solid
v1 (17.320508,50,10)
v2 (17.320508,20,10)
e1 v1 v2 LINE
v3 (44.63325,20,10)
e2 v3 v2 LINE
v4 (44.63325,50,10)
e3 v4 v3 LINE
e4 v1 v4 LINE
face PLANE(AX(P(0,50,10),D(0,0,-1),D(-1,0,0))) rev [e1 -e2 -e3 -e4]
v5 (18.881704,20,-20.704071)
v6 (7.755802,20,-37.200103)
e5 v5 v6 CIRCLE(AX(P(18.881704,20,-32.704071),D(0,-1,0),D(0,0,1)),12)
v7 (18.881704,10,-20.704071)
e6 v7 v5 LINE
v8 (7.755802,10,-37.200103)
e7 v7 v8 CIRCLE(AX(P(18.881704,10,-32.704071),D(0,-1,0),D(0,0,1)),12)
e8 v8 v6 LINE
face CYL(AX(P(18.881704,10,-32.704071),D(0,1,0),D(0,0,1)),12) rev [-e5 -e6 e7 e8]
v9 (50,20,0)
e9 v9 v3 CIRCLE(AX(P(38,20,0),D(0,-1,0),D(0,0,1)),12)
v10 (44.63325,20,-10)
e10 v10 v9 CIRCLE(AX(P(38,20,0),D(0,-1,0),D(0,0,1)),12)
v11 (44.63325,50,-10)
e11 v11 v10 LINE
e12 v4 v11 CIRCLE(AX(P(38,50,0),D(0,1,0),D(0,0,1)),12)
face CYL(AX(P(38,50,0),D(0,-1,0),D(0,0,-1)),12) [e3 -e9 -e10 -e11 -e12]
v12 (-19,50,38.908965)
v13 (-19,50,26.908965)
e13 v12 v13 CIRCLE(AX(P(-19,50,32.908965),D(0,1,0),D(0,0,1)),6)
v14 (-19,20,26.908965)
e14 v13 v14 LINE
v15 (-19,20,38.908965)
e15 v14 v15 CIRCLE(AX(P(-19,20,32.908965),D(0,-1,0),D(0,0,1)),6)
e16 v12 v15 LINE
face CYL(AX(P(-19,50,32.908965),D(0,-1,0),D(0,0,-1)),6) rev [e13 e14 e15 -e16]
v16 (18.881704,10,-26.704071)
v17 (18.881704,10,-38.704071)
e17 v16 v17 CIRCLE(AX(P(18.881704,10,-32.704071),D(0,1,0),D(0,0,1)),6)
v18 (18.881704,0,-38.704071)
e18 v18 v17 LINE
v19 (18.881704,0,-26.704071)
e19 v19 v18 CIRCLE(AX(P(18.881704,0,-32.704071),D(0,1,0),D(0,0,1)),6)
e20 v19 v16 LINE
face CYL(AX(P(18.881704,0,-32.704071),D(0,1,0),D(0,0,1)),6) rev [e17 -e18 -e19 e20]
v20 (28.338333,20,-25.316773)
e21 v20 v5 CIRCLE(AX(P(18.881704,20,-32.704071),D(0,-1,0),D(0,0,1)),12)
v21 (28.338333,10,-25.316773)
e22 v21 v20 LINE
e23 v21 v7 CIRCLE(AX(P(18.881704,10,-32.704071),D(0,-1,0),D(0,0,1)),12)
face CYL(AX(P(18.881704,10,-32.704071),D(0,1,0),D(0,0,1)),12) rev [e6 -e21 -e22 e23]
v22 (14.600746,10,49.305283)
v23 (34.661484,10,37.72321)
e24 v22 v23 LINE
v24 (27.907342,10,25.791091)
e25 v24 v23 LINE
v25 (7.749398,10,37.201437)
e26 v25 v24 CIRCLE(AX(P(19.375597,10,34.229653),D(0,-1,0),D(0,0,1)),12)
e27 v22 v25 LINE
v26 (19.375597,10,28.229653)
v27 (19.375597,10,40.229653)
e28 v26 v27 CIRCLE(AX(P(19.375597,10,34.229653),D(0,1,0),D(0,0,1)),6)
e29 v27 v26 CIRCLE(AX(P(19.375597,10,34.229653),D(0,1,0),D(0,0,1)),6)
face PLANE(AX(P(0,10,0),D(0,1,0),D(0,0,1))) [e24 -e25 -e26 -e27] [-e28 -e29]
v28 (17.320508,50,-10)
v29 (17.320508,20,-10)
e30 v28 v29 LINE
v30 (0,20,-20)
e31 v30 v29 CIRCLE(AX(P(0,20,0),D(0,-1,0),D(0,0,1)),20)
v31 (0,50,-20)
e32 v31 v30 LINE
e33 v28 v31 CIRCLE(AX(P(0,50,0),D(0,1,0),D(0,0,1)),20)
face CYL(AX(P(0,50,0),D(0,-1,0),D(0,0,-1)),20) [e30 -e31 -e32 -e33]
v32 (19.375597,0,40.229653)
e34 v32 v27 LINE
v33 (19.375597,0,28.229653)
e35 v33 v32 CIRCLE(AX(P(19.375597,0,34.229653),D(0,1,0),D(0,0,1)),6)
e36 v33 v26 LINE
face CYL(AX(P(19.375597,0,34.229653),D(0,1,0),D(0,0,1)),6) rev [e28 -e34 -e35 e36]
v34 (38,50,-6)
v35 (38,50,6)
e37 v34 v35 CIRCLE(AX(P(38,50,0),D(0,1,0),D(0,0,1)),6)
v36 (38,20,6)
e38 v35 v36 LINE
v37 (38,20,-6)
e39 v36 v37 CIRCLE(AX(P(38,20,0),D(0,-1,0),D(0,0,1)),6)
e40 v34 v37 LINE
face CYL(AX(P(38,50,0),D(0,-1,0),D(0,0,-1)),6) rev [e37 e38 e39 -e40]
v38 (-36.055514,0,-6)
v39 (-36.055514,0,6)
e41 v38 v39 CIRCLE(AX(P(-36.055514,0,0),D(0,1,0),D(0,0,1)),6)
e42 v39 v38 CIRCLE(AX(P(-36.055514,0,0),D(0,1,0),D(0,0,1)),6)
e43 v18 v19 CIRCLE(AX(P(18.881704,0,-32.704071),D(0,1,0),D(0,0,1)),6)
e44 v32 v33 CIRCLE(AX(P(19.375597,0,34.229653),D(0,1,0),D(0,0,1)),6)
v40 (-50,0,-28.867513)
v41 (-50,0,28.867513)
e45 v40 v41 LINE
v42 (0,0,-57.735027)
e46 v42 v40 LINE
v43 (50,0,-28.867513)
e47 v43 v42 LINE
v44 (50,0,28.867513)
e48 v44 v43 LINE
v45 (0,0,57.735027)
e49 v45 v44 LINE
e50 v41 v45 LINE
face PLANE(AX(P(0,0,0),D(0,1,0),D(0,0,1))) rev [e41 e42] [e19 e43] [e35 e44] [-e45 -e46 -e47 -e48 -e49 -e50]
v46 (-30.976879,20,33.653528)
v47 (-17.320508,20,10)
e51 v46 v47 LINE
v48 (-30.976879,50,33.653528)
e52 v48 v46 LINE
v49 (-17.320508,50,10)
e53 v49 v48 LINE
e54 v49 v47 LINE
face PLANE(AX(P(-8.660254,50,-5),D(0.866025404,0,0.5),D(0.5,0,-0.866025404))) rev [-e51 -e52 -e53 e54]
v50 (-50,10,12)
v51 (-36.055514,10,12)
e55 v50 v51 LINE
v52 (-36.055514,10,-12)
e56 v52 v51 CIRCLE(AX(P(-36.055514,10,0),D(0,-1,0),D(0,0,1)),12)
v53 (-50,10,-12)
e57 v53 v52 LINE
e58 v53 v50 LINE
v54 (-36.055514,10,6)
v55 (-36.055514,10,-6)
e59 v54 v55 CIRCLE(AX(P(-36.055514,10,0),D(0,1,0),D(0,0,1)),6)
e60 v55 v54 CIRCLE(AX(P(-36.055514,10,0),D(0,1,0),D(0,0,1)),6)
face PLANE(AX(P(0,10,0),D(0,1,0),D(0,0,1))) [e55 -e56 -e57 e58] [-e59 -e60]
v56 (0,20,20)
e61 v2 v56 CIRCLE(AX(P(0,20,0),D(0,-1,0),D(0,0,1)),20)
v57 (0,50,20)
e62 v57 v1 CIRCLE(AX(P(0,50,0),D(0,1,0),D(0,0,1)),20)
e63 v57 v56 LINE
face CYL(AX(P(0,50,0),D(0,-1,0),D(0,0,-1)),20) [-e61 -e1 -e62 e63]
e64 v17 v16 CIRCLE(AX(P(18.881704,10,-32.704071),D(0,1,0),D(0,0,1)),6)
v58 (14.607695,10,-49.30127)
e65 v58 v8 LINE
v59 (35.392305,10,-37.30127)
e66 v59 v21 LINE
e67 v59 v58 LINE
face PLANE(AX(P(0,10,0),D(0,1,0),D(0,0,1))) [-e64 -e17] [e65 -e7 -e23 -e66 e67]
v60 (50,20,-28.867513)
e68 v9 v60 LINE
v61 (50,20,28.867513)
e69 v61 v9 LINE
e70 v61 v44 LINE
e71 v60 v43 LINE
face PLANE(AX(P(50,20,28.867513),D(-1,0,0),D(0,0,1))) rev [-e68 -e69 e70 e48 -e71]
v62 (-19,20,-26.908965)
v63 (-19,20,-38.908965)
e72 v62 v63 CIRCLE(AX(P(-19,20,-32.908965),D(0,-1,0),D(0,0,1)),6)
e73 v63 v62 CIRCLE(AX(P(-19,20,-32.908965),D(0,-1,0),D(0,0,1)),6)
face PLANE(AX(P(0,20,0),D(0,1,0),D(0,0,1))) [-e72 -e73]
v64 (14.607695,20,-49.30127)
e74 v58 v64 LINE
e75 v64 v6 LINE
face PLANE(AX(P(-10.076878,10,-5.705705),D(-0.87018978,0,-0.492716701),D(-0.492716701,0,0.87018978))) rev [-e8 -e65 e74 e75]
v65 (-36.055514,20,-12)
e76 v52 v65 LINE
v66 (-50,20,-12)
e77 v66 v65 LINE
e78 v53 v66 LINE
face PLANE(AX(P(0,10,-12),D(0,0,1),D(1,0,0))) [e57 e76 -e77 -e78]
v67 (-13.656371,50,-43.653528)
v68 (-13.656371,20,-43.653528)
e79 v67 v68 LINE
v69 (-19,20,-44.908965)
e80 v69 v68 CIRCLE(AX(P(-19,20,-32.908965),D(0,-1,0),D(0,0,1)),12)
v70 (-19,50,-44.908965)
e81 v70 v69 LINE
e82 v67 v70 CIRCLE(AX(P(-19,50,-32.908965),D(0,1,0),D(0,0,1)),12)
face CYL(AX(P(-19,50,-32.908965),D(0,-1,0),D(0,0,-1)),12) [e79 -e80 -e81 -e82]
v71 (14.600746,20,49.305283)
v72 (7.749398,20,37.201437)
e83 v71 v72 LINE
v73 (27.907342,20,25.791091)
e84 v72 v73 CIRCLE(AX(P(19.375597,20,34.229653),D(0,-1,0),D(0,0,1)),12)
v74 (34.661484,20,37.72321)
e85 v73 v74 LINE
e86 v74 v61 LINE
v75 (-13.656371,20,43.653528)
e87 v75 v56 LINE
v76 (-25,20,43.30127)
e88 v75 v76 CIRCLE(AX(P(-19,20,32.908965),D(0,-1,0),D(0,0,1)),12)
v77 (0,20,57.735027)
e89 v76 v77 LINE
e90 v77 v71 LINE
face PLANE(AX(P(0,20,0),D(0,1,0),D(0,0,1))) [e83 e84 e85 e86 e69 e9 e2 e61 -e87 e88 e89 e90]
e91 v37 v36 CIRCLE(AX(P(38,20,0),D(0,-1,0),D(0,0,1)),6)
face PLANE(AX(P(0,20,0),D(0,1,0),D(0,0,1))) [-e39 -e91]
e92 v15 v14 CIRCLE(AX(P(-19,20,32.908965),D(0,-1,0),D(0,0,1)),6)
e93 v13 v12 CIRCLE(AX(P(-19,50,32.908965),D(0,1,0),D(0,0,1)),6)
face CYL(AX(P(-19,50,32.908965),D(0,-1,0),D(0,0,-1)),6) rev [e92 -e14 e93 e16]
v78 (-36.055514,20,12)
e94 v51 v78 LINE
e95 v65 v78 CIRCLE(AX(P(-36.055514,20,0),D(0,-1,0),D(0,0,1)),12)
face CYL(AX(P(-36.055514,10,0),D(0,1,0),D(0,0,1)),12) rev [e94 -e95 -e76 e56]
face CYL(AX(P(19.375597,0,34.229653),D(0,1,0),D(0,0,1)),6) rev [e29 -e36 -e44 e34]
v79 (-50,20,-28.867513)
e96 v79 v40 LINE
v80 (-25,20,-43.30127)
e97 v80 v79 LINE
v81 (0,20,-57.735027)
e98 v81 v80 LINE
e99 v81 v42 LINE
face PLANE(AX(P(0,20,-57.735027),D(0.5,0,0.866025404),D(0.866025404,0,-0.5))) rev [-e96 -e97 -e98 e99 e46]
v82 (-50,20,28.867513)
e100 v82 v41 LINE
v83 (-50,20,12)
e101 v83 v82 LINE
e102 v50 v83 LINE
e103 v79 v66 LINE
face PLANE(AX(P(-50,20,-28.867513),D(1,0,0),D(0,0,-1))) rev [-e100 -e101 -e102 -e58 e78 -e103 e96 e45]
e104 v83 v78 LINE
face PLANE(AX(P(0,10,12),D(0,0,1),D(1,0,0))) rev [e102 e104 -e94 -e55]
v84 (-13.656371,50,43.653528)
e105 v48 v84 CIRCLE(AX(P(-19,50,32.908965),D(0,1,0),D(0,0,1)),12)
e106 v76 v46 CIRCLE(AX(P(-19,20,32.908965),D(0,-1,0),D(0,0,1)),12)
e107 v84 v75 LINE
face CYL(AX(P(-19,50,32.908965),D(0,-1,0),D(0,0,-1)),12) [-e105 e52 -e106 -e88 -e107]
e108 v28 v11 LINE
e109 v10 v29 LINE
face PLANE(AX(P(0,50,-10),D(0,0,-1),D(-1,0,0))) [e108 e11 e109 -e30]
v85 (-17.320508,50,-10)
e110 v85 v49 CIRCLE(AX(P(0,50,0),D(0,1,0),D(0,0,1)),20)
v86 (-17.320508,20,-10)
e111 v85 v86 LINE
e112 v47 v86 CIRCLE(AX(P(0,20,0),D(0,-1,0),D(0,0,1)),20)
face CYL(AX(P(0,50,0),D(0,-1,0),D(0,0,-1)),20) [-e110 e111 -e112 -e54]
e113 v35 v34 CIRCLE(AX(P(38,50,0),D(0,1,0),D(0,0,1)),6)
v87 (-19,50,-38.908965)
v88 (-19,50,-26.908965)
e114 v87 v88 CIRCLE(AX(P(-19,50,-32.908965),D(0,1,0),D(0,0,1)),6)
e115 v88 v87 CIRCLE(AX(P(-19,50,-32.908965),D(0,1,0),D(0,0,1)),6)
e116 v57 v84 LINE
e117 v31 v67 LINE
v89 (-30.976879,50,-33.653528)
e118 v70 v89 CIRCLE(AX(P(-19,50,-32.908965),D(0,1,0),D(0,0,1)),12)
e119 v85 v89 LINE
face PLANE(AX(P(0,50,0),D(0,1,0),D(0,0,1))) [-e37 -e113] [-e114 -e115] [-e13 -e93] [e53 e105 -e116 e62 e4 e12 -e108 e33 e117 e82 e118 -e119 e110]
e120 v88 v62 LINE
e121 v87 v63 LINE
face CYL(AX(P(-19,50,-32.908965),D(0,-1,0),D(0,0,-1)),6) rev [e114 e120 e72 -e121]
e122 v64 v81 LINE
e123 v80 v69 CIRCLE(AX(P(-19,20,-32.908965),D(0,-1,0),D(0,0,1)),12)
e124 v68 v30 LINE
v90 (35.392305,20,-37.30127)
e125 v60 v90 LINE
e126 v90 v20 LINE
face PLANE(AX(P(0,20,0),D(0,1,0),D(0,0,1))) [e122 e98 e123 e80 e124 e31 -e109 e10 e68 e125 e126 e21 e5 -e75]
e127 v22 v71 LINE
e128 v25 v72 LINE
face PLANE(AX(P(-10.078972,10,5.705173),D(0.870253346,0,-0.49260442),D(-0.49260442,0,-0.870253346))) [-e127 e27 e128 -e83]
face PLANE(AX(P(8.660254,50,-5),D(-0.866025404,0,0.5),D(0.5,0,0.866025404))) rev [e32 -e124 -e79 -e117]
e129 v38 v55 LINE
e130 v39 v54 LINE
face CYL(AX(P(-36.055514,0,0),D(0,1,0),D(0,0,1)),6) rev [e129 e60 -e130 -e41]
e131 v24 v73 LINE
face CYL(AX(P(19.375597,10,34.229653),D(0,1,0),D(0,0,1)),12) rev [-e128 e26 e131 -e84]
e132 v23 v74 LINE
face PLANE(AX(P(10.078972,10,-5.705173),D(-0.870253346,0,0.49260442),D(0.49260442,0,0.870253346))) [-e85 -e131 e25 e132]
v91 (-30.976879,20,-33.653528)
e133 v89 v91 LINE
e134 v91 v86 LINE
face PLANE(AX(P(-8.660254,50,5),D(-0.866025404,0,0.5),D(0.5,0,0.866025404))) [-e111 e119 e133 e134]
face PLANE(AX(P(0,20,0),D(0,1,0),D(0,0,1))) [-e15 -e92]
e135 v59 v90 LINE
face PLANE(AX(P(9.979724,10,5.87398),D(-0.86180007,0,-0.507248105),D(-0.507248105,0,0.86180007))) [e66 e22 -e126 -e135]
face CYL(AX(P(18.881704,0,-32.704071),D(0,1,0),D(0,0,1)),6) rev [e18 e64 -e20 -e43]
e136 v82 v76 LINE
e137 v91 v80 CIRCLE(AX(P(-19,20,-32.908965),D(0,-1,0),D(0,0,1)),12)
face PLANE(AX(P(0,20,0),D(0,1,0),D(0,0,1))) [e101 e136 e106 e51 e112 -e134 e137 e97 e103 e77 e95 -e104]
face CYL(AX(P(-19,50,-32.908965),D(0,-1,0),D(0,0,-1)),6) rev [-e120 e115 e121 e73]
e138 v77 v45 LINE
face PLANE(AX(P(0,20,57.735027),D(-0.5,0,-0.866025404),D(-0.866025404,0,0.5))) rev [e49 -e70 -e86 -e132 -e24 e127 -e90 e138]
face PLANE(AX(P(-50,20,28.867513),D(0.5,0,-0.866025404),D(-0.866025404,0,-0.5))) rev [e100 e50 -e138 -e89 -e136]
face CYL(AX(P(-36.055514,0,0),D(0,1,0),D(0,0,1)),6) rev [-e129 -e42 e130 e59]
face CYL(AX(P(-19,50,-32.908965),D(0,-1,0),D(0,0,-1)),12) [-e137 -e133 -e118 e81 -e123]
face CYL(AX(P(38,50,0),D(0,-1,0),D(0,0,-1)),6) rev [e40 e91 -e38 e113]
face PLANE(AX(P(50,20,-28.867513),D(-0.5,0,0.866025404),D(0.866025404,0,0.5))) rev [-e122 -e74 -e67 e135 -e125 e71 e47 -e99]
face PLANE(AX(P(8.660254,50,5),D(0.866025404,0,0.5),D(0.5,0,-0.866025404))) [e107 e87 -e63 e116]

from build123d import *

# Parameters (mm, degrees)
HEX_BASE_100AF_X20_DEPTH    = 20
EDGE_POCKET_SKETCH_R        = 6
EDGE_POCKETS_DEPTH_10_DEPTH = 10
THREE_ARM_BOSS_SKETCH_R     = 6
THREE_ARM_BOSS_H50_DEPTH    = 50
POCKET_HOLE_SKETCH_R        = 6
POCKET_THROUGH_HOLES_DEPTH  = 10


with BuildPart() as part:
    # Hex Base Sketch → Hex Base 100AF x20 (new body)
    with BuildSketch(Plane(origin=(0, 0, 0), x_dir=(1, 0, 0), z_dir=(0, 1, 0))):
        Polygon((0, 57.735026919), (-50, 28.867513459), (-50, -28.867513459), (0, -57.735026919), (50, -28.867513459), (50, 28.867513459), align=None)
    extrude(amount=HEX_BASE_100AF_X20_DEPTH)

    # Edge Pocket Sketch → Edge Pockets Depth 10 (cut)
    # profile 1 of 6: a face of its own
    with BuildSketch(Plane(origin=(0, 20, 0), x_dir=(1, 0, 0), z_dir=(0, 1, 0))):
        with BuildLine():
            Line((-50, 12), (-50, -12))
            Line((-50, -12), (-36.055514092, -12))
            ThreePointArc((-36.055514092, -12), (-24.055514092, 0), (-36.055514092, 12))
            Line((-36.055514092, 12), (-50, 12))
        make_face()
        with Locations((-38.000001269, 0)):
            Circle(EDGE_POCKET_SKETCH_R, mode=Mode.SUBTRACT)
    # profile 2 of 6: a face of its own
    with BuildSketch(Plane(origin=(0, 20, 0), x_dir=(1, 0, 0), z_dir=(0, 1, 0))):
        with BuildLine():
            Line((35.392304845, 37.301270189), (14.607695155, 49.301270189))
            Line((14.607695155, 49.301270189), (7.755802012, 37.200102575))
            ThreePointArc((7.755802012, 37.200102575), (12.881704296, 22.311766329), (28.338332848, 25.316772856))
            Line((28.338332848, 25.316772856), (35.392304845, 37.301270189))
        make_face()
        with Locations((19.000000635, 32.908966443)):
            Circle(EDGE_POCKET_SKETCH_R, mode=Mode.SUBTRACT)
    # profile 3 of 6: a face of its own
    with BuildSketch(Plane(origin=(0, 20, 0), x_dir=(1, 0, 0), z_dir=(0, 1, 0))):
        with BuildLine():
            ThreePointArc((27.907341935, -25.791090759), (21.025211471, -22.343578273), (13.464344244, -23.786612875))
            ThreePointArc((13.464344244, -23.786612875), (8.335672837, -29.526455354), (7.749398434, -37.201437074))
            Line((7.749398434, -37.201437074), (8.639996816, -38.774801402))
            Line((8.639996816, -38.774801402), (14.600745568, -49.305282535))
            Line((14.600745568, -49.305282535), (34.661483865, -37.723209879))
            Line((34.661483865, -37.723209879), (28.797940317, -27.364455088))
            Line((28.797940317, -27.364455088), (27.907341935, -25.791090759))
        make_face()
        with BuildLine():
            ThreePointArc((24.718968567, -33.069628245), (15.696863266, -38.252955318), (15.763342049, -27.84810817))
            ThreePointArc((15.763342049, -27.84810817), (21.741073867, -27.886301171), (24.718968567, -33.069628245))
        make_face(mode=Mode.SUBTRACT)
    # profile 4 of 6: a face of its own
    with BuildSketch(Plane(origin=(0, 20, 0), x_dir=(1, 0, 0), z_dir=(0, 1, 0))):
        with Locations((18.718968567, -33.069628245)):
            Circle(EDGE_POCKET_SKETCH_R)
    # profile 5 of 6: a face of its own
    with BuildSketch(Plane(origin=(0, 20, 0), x_dir=(1, 0, 0), z_dir=(0, 1, 0))):
        with Locations((-38.000001269, 0)):
            Circle(EDGE_POCKET_SKETCH_R)
    # profile 6 of 6: a face of its own
    with BuildSketch(Plane(origin=(0, 20, 0), x_dir=(1, 0, 0), z_dir=(0, 1, 0))):
        with Locations((19.000000635, 32.908966443)):
            Circle(EDGE_POCKET_SKETCH_R)
    extrude(amount=-EDGE_POCKETS_DEPTH_10_DEPTH, mode=Mode.SUBTRACT)

    # Three-Arm Boss Sketch → Three-Arm Boss H50 (add)
    # profile 1 of 2: a face of its own
    with BuildSketch(Plane(origin=(0, 0, 0), x_dir=(1, 0, 0), z_dir=(0, 1, 0))):
        with BuildLine():
            ThreePointArc((0, -20), (10, -17.320508076), (17.320508076, -10))
            Line((17.320508076, -10), (25, -10))
            Line((25, -10), (25, 10))
            Line((25, 10), (17.320508076, 10))
            ThreePointArc((17.320508076, 10), (10, 17.320508076), (0, 20))
            Line((0, 20), (-13.656370753, 43.65352799))
            ThreePointArc((-13.656370753, 43.65352799), (-25, 43.301270189), (-30.976878828, 33.65352799))
            Line((-30.976878828, 33.65352799), (-17.320508076, 10))
            ThreePointArc((-17.320508076, 10), (-20, 0), (-17.320508076, -10))
            Line((-17.320508076, -10), (-30.976878828, -33.65352799))
            ThreePointArc((-30.976878828, -33.65352799), (-25, -43.301270189), (-13.656370753, -43.65352799))
            Line((-13.656370753, -43.65352799), (0, -20))
        make_face()
        with Locations(Location((-19, -32.908965344, 0), (0, 0, 270))):
            Circle(THREE_ARM_BOSS_SKETCH_R, mode=Mode.SUBTRACT)
        with Locations(Location((-19, 32.908965344, 0), (0, 0, 270))):
            Circle(THREE_ARM_BOSS_SKETCH_R, mode=Mode.SUBTRACT)
    # profile 2 of 2: a face of its own
    with BuildSketch(Plane(origin=(0, 0, 0), x_dir=(1, 0, 0), z_dir=(0, 1, 0))):
        with BuildLine():
            Line((25, 10), (25, -10))
            Line((25, -10), (44.633249581, -10))
            ThreePointArc((44.633249581, -10), (50, 0), (44.633249581, 10))
            Line((44.633249581, 10), (25, 10))
        make_face()
        with Locations(Location((38, 0, 0), (0, 0, 270))):
            Circle(THREE_ARM_BOSS_SKETCH_R, mode=Mode.SUBTRACT)
    extrude(amount=THREE_ARM_BOSS_H50_DEPTH)

    # Pocket Hole Sketch → Pocket Through Holes (cut)
    with BuildSketch(Plane(origin=(0, 10, 0), x_dir=(1, 0, 0), z_dir=(0, 1, 0))):
        with Locations(Location((19.375597278, -34.229653025, 0), (0, 0, 270))):
            Circle(POCKET_HOLE_SKETCH_R)
        with Locations(Location((-36.055514092, 0, 0), (0, 0, 270))):
            Circle(POCKET_HOLE_SKETCH_R)
        with Locations(Location((18.881704296, 32.704071174, 0), (0, 0, 270))):
            Circle(POCKET_HOLE_SKETCH_R)
    extrude(amount=-POCKET_THROUGH_HOLES_DEPTH, mode=Mode.SUBTRACT)


solid = part.part
